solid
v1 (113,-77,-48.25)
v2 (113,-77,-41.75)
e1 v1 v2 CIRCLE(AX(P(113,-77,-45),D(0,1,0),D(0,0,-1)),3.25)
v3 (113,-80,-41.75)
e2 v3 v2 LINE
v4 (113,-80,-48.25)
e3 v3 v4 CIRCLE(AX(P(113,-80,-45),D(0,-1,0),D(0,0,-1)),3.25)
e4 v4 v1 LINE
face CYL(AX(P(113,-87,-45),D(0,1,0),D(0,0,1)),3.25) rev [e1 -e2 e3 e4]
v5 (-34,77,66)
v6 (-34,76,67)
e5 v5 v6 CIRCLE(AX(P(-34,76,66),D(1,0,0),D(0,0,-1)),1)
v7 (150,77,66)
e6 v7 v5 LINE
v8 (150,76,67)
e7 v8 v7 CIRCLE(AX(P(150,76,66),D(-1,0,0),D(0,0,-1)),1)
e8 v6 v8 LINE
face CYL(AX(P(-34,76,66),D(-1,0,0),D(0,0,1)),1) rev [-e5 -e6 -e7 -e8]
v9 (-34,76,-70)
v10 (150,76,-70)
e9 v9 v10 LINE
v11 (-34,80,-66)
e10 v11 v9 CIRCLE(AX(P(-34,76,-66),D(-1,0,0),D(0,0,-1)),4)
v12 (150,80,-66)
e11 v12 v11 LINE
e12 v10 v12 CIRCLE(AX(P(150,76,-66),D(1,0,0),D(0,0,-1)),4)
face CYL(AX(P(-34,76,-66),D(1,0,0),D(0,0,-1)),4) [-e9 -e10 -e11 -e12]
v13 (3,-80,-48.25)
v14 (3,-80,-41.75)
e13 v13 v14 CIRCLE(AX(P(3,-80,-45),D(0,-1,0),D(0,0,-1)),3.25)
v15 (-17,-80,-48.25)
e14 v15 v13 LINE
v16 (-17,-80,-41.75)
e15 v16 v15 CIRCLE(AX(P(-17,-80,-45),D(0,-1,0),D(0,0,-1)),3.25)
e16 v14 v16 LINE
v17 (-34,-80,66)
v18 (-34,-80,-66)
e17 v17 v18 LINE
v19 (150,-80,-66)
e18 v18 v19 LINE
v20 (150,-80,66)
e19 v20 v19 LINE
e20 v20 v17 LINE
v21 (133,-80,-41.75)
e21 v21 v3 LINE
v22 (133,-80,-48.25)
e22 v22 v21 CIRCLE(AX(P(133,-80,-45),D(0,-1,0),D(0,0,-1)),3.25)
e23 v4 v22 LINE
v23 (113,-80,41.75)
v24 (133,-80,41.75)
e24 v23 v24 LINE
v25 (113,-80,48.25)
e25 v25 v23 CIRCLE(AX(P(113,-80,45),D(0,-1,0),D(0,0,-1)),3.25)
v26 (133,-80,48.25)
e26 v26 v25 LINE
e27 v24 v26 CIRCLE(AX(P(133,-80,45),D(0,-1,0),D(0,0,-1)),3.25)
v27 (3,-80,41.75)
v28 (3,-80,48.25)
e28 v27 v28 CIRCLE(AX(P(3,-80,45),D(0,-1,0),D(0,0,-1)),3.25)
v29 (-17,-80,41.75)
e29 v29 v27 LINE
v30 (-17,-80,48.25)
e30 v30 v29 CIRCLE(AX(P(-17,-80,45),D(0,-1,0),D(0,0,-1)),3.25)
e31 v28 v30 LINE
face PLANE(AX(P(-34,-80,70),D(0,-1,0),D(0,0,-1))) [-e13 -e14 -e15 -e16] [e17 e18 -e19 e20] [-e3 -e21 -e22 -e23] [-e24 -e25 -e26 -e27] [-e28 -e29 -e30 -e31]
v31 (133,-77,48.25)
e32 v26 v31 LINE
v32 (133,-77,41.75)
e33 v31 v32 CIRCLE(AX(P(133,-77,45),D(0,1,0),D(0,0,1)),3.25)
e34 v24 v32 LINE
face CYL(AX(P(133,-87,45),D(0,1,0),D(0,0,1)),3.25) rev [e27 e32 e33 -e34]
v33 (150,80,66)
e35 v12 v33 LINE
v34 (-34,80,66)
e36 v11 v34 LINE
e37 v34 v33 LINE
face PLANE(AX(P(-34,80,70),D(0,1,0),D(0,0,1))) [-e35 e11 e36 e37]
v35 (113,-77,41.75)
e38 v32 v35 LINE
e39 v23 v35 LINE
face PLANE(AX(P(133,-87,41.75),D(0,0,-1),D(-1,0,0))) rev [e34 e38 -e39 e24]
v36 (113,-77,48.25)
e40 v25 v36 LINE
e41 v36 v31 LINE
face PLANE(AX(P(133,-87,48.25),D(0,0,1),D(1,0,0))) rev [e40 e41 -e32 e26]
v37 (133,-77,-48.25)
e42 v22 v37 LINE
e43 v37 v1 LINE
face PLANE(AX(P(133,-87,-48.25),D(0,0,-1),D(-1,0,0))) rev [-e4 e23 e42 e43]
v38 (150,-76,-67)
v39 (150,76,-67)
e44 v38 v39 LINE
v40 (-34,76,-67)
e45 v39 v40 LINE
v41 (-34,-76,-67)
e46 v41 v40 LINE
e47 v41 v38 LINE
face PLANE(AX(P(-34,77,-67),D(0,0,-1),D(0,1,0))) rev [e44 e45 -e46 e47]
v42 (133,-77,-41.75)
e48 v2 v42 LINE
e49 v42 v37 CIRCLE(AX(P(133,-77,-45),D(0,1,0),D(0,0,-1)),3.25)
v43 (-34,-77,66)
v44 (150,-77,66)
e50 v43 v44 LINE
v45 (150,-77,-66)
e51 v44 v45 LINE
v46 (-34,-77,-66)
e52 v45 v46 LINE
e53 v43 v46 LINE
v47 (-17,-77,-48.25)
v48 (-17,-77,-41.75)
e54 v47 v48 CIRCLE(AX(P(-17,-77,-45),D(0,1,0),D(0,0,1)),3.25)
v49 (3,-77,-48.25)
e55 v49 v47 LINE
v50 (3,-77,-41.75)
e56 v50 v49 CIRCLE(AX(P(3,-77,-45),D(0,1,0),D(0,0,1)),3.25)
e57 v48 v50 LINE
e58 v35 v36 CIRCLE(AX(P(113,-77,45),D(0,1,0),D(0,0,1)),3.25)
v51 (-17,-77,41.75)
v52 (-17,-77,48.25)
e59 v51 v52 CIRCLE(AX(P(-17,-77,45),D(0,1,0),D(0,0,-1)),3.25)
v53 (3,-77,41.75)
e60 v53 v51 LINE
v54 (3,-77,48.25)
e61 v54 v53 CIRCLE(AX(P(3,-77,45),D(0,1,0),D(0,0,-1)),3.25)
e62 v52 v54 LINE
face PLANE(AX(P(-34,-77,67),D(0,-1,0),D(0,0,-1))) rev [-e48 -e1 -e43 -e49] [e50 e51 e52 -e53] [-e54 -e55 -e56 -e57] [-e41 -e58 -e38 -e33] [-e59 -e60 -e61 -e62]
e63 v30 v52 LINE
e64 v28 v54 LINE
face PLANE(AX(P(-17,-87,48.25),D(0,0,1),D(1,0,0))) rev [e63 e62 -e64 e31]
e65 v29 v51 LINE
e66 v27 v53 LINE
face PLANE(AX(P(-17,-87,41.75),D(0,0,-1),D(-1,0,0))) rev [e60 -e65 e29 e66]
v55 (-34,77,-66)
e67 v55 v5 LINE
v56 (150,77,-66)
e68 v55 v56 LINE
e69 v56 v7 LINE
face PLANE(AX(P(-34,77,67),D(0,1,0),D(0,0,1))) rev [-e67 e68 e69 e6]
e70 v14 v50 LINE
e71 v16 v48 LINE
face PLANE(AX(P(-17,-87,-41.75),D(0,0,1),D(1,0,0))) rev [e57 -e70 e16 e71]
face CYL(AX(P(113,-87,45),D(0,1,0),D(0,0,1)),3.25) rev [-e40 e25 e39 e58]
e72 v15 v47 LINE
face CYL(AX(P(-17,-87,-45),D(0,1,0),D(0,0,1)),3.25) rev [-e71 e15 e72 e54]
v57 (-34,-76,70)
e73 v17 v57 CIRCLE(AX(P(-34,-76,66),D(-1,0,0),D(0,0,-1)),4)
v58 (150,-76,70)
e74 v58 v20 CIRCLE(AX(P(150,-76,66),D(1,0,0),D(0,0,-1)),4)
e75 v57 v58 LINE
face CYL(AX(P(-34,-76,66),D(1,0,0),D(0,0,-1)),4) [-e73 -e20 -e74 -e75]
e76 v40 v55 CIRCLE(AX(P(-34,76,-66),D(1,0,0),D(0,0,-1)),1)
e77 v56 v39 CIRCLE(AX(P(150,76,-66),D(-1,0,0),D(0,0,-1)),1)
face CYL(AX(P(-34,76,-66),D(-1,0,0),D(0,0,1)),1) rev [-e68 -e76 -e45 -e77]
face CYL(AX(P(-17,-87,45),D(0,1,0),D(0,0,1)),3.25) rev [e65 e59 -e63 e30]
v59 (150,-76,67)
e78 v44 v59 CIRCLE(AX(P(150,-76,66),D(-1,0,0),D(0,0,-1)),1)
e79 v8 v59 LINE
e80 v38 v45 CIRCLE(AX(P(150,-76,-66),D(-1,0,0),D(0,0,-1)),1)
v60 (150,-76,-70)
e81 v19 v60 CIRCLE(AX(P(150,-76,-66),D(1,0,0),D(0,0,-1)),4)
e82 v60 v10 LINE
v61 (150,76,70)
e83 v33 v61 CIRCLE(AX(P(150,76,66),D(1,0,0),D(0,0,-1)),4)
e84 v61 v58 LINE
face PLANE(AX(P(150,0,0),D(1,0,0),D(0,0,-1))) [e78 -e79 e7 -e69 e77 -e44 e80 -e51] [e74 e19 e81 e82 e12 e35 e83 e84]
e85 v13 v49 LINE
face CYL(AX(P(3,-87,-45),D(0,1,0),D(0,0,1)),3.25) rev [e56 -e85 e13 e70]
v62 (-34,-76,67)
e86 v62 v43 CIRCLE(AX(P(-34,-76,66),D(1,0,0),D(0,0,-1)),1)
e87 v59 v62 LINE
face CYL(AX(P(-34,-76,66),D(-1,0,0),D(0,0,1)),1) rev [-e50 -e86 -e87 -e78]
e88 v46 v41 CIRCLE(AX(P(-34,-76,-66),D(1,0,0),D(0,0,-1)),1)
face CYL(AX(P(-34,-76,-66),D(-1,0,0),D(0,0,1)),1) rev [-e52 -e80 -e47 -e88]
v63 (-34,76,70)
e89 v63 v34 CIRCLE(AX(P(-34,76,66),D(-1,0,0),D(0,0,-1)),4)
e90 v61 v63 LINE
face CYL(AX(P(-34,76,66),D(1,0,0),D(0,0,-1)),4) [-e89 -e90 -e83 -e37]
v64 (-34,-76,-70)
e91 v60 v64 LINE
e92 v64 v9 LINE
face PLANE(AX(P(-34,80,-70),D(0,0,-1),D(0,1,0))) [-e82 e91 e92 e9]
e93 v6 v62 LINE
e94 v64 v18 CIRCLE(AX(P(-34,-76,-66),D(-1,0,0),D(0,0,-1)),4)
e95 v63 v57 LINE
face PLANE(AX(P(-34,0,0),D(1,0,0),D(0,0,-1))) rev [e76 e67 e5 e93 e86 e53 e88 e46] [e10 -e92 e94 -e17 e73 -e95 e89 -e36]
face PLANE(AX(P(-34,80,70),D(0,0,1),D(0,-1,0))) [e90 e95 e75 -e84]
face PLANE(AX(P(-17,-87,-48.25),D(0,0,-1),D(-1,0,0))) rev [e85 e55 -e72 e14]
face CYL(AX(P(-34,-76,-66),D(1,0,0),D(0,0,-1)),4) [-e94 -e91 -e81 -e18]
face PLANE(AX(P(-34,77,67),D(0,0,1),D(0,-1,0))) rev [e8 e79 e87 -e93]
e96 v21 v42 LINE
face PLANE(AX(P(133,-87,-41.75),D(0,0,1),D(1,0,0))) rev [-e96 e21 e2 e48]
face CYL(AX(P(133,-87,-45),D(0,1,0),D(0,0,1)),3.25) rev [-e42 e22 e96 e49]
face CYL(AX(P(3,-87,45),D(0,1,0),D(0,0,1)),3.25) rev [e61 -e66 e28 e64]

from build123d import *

# Parameters (mm, degrees)
EXTRUDE_1_DEPTH      = 150
EXTRUDE_1_DEPTH_BACK = 34
SKETCH_2_W           = 140
SKETCH_2_H           = 160
SKETCH_2_W_2         = 134
SKETCH_2_H_2         = 154
CUT_EXTRUDE_1_DEPTH  = 10
FILLET_1_R           = 1
FILLET_2_R           = 4


with BuildPart() as part:
    # 草图2 → 凸台-拉伸1 (new, two sides: drawn at the far end of the back side and taken through both)
    with BuildSketch(Plane(origin=(0, 0, 0), x_dir=(0, 0, -1), z_dir=(1, 0, 0)).offset(-EXTRUDE_1_DEPTH_BACK)):
        Rectangle(SKETCH_2_W, SKETCH_2_H)
        Rectangle(SKETCH_2_W_2, SKETCH_2_H_2, mode=Mode.SUBTRACT)
    extrude(amount=EXTRUDE_1_DEPTH + EXTRUDE_1_DEPTH_BACK)

    # 草图3 → 切除-拉伸1 (cut)
    with BuildSketch(Plane(origin=(0, -77, 0), x_dir=(1, 0, 0), z_dir=(0, 1, 0))):
        with BuildLine():
            Line((-17, 48.25), (3, 48.25))
            ThreePointArc((3, 48.25), (6.25, 45), (3, 41.75))
            Line((3, 41.75), (-17, 41.75))
            ThreePointArc((-17, 41.75), (-20.25, 45), (-17, 48.25))
        make_face()
        with BuildLine():
            Line((-17, -48.25), (3, -48.25))
            ThreePointArc((3, -48.25), (6.25, -45), (3, -41.75))
            Line((3, -41.75), (-17, -41.75))
            ThreePointArc((-17, -41.75), (-20.25, -45), (-17, -48.25))
        make_face()
        with BuildLine():
            Line((133, 48.25), (113, 48.25))
            ThreePointArc((113, 48.25), (109.75, 45), (113, 41.75))
            Line((113, 41.75), (133, 41.75))
            ThreePointArc((133, 41.75), (136.25, 45), (133, 48.25))
        make_face()
        with BuildLine():
            Line((133, -48.25), (113, -48.25))
            ThreePointArc((113, -48.25), (109.75, -45), (113, -41.75))
            Line((113, -41.75), (133, -41.75))
            ThreePointArc((133, -41.75), (136.25, -45), (133, -48.25))
        make_face()
    extrude(amount=-CUT_EXTRUDE_1_DEPTH, mode=Mode.SUBTRACT)

    # 圆角1
    fillet_1_edges = [part.edges().sort_by_distance(p)[0] for p in [
        (58, -77, 67),
        (58, 77, 67),
        (58, 77, -67),
        (58, -77, -67),
    ]]
    fillet(fillet_1_edges, radius=FILLET_1_R)

    # 圆角2
    fillet_2_edges = [part.edges().sort_by_distance(p)[0] for p in [
        (58, -80, -70),
        (58, -80, 70),
        (58, 80, 70),
        (58, 80, -70),
    ]]
    fillet(fillet_2_edges, radius=FILLET_2_R)


solid = part.part
